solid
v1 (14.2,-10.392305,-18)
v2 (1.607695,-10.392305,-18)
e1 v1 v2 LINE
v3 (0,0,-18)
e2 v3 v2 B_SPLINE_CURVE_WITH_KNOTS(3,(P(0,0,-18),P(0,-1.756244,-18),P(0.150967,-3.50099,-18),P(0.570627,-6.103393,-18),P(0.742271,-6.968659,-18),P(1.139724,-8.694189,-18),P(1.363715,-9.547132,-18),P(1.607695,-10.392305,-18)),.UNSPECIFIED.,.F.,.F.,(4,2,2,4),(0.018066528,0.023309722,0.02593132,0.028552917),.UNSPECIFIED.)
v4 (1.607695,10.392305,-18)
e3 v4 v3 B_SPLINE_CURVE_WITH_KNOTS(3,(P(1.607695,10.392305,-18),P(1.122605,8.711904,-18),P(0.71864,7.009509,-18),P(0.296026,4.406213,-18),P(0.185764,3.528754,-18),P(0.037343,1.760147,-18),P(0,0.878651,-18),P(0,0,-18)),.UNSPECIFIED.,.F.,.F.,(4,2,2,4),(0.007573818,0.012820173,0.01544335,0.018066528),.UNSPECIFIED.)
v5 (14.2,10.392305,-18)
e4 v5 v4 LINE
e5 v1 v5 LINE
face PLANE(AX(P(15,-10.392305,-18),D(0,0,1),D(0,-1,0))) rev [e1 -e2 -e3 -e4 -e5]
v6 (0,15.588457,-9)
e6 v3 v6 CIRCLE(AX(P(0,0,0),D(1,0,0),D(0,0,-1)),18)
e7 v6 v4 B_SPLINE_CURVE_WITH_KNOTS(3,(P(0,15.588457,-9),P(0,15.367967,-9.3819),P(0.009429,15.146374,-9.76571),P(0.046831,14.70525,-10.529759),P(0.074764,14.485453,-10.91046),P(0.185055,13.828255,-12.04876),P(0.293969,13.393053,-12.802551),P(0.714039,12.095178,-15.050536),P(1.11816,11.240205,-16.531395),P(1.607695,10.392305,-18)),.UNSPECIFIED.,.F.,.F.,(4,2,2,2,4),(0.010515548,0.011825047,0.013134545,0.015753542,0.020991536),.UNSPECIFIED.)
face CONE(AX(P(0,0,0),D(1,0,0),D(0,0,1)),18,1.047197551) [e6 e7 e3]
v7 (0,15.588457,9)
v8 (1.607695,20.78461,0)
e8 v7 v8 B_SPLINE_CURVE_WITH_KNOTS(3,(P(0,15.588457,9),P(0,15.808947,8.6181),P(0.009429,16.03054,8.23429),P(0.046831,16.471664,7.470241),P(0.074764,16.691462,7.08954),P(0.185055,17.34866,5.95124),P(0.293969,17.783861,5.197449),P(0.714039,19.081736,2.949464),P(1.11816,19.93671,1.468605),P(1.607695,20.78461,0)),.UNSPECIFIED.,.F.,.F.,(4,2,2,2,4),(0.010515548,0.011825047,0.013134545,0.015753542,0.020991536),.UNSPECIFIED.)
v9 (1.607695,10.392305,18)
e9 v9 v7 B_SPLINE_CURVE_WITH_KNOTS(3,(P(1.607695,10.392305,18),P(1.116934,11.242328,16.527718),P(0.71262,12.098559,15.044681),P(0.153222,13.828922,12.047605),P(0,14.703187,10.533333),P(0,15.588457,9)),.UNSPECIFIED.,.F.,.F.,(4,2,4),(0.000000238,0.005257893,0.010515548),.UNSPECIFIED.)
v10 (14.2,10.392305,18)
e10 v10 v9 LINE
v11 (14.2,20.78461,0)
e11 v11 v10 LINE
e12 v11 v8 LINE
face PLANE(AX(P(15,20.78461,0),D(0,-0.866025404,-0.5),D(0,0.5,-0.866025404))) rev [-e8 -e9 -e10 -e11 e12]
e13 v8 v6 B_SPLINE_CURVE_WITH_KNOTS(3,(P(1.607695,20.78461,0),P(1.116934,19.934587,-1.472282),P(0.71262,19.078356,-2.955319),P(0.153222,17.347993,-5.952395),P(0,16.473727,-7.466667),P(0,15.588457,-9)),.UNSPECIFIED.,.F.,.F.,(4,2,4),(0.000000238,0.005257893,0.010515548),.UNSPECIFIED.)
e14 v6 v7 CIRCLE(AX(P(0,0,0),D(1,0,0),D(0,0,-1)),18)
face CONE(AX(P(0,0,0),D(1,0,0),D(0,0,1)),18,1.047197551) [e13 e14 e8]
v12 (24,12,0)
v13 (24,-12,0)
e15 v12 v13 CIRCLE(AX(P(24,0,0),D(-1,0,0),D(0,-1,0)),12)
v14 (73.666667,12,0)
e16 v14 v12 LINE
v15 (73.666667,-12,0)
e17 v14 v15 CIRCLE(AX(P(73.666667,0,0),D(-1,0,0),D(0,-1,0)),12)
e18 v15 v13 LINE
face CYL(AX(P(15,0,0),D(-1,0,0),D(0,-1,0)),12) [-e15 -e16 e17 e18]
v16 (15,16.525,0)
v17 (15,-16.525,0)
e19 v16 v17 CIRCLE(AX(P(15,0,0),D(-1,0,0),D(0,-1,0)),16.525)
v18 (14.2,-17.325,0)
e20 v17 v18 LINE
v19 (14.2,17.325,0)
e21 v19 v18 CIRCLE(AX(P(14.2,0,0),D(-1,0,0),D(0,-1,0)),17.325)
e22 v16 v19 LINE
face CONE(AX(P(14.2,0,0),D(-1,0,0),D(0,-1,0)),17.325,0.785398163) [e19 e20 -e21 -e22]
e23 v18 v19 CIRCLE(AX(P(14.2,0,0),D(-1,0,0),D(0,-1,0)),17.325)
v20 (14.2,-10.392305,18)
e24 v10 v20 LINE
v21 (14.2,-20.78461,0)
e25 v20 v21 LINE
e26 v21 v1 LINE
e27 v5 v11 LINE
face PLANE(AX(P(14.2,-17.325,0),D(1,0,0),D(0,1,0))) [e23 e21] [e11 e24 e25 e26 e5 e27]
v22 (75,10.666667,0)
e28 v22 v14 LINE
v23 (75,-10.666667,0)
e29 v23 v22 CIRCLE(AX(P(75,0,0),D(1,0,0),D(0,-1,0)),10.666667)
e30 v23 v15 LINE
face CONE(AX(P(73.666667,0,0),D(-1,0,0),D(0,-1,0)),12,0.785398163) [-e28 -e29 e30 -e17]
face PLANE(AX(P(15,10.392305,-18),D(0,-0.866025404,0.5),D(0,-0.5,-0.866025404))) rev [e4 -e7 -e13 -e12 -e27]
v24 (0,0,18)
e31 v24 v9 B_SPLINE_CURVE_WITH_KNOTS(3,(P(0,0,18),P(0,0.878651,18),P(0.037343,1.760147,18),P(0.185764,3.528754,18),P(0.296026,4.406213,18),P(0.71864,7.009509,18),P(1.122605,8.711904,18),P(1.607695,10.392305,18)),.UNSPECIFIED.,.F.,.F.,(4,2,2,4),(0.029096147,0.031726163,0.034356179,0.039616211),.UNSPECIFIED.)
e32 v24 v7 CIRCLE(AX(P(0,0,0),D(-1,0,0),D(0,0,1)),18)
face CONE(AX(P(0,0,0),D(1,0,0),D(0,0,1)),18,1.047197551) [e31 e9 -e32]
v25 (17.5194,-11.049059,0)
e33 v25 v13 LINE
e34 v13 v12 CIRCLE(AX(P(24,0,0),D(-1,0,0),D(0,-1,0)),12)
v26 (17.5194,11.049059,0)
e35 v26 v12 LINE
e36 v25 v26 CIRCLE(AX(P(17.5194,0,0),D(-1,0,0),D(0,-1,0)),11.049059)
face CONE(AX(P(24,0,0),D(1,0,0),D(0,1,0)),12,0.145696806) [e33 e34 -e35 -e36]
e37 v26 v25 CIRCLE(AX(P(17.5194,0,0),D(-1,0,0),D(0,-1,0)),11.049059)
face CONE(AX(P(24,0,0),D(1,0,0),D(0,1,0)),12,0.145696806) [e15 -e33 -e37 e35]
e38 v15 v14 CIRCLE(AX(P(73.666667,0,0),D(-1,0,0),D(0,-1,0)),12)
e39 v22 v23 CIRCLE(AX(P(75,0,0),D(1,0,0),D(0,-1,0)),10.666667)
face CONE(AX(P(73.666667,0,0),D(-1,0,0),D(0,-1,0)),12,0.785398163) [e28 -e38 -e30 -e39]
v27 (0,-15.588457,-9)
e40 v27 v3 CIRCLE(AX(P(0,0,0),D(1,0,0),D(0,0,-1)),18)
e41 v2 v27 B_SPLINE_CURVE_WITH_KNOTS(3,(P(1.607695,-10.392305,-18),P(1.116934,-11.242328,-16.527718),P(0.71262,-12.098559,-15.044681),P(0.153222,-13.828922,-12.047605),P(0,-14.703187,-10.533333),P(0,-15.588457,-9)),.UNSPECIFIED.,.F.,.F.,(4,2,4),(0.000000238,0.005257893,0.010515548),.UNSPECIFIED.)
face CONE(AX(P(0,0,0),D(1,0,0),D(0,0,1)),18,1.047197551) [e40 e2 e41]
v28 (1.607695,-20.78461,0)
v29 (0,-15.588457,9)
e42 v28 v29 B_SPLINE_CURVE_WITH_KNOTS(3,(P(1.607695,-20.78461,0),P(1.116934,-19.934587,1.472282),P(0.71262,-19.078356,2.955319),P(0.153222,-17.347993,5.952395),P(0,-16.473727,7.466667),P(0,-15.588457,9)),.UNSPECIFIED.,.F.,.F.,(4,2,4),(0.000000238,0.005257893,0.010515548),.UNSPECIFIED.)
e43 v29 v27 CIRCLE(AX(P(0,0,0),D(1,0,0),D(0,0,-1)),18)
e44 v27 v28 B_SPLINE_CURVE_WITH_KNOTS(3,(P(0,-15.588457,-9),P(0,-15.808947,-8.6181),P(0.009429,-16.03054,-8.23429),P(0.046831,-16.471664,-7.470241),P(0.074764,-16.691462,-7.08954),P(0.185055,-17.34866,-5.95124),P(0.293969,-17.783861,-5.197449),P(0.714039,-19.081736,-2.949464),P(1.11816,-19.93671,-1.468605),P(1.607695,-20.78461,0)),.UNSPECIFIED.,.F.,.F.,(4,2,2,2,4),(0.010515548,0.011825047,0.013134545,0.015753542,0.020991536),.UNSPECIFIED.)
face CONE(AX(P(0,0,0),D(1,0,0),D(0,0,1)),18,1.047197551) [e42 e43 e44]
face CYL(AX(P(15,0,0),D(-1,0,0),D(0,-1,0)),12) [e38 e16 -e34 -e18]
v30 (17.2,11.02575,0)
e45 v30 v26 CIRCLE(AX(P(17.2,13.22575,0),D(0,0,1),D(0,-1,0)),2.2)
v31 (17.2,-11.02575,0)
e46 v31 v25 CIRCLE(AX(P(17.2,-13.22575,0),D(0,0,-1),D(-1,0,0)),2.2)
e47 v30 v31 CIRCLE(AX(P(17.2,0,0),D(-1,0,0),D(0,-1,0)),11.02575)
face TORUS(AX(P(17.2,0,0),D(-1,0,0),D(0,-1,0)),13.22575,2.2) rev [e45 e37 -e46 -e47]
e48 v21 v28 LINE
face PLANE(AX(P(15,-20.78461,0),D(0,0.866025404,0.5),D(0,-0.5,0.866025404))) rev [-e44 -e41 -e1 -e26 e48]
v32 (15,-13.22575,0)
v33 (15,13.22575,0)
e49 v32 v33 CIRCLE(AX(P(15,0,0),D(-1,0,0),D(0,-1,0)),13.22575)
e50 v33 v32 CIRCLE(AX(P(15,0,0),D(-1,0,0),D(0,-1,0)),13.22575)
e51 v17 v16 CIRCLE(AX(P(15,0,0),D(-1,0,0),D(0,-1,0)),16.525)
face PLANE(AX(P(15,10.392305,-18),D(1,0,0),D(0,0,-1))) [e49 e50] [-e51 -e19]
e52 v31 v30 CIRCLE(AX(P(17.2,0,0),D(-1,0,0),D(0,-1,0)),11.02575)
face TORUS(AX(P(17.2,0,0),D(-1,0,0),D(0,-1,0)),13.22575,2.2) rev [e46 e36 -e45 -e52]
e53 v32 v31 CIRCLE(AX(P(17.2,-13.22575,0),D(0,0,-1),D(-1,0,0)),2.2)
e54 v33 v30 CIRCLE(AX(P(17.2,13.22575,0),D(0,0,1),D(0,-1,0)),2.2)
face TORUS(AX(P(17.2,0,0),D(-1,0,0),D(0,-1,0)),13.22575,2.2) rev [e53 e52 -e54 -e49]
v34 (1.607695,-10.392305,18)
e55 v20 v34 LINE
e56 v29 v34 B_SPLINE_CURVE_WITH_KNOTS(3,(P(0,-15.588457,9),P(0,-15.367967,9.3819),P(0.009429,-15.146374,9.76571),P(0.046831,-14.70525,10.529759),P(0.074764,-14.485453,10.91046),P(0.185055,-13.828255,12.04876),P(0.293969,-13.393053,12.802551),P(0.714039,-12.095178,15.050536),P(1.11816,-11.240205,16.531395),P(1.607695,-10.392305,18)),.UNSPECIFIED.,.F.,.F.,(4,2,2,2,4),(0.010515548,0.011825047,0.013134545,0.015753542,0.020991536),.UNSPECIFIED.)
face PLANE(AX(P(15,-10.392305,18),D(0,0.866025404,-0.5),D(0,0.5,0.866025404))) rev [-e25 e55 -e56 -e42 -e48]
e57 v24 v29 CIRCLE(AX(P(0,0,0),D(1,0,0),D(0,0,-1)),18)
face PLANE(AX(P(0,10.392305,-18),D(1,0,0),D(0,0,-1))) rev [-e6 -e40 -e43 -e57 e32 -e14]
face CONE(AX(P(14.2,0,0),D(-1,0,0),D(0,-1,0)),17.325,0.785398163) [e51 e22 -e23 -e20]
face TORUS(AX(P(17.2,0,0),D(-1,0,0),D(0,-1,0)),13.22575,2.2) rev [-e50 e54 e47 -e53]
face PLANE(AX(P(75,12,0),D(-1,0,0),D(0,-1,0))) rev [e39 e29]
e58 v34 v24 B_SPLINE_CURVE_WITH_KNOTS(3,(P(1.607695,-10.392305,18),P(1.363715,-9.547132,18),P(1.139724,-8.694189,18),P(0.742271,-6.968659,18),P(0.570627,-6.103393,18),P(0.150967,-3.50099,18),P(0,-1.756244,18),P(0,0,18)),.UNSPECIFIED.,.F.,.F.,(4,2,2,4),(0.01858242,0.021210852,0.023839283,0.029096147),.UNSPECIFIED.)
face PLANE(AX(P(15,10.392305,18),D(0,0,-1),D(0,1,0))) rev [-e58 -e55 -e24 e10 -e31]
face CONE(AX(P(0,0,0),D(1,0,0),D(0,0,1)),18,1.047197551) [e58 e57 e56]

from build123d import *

# Parameters (mm, degrees)
EXTRUDE_1_DEPTH     = 15
SKETCH_4_R          = 39.55
SKETCH_4_R_2        = 18
CUT_EXTRUDE_1_DEPTH = 1.875
CUT_EXTRUDE_1_DRAFT = -60
CHAMFER_1_SIZE      = 1.333333333


with BuildPart() as part:
    # 草图3 → 凸台-拉伸1 (new body)
    with BuildSketch(Plane(origin=(0, 0, 0), x_dir=(0, 0, -1), z_dir=(1, 0, 0))):
        Polygon((18, 10.392304845), (0, 20.784609691), (-18, 10.392304845), (-18, -10.392304845), (0, -20.784609691), (18, -10.392304845), align=None)
    extrude(amount=EXTRUDE_1_DEPTH)


with BuildPart() as cut_extrude_1_tool:
    # 草图4 → 切除-拉伸1 (with draft: the straight prism first)
    with BuildSketch(Plane.ZY):
        Circle(SKETCH_4_R)
        Circle(SKETCH_4_R_2, mode=Mode.SUBTRACT)
    extrude(amount=-CUT_EXTRUDE_1_DEPTH)
    # 切除-拉伸1: the draft: its side faces are tilted about the plane it starts from
    cut_extrude_1_sides = [cut_extrude_1_tool.faces().sort_by_distance(p)[0] for p in [
        (0.9375, 0, -39.55),
        (0.9375, 0, -18),
    ]]
    draft(cut_extrude_1_sides, Plane.ZY, CUT_EXTRUDE_1_DRAFT)


with BuildPart() as part_1:
    add(part.part)

    # 切除-拉伸1: cut by cut_extrude_1_tool
    add(cut_extrude_1_tool.part, mode=Mode.SUBTRACT)

    # 草图6 → 旋转2 (revolve)
    with BuildSketch(Plane.XY, mode=Mode.PRIVATE) as revolve_2_sk:
        with BuildLine():
            Line((24, 12), (75, 12))
            Line((75, 12), (75, 0))
            Line((75, 0), (15, 0))
            Line((15, 0), (15, 13.22575))
            ThreePointArc((15, 13.22575), (15.76171636, 11.561015736), (17.519400155, 11.049059039))
            Line((17.519400155, 11.049059039), (24, 12))
        make_face()
    revolve(revolve_2_sk.sketch.rotate(Axis((15, 0, 0), (1, 0, 0)), 180), axis=Axis((15, 0, 0), (1, 0, 0)))

    # 倒角1
    chamfer_1_edges = [part_1.edges().sort_by_distance(p)[0] for p in [
        (75, 12, 0),
    ]]
    chamfer(chamfer_1_edges, length=CHAMFER_1_SIZE)

    # 草图8 → 切除-旋转2 (revolve, cut)
    with BuildSketch(Plane.XY, mode=Mode.PRIVATE) as cut_revolve_2_sk:
        Polygon((15, 16.525), (14.2, 17.325), (14.2, 39.55), (15, 39.55), align=None)
    revolve(cut_revolve_2_sk.sketch.rotate(Axis((0, 0, 0), (1, 0, 0)), 180), axis=Axis((0, 0, 0), (1, 0, 0)), mode=Mode.SUBTRACT)


solid = part_1.part
